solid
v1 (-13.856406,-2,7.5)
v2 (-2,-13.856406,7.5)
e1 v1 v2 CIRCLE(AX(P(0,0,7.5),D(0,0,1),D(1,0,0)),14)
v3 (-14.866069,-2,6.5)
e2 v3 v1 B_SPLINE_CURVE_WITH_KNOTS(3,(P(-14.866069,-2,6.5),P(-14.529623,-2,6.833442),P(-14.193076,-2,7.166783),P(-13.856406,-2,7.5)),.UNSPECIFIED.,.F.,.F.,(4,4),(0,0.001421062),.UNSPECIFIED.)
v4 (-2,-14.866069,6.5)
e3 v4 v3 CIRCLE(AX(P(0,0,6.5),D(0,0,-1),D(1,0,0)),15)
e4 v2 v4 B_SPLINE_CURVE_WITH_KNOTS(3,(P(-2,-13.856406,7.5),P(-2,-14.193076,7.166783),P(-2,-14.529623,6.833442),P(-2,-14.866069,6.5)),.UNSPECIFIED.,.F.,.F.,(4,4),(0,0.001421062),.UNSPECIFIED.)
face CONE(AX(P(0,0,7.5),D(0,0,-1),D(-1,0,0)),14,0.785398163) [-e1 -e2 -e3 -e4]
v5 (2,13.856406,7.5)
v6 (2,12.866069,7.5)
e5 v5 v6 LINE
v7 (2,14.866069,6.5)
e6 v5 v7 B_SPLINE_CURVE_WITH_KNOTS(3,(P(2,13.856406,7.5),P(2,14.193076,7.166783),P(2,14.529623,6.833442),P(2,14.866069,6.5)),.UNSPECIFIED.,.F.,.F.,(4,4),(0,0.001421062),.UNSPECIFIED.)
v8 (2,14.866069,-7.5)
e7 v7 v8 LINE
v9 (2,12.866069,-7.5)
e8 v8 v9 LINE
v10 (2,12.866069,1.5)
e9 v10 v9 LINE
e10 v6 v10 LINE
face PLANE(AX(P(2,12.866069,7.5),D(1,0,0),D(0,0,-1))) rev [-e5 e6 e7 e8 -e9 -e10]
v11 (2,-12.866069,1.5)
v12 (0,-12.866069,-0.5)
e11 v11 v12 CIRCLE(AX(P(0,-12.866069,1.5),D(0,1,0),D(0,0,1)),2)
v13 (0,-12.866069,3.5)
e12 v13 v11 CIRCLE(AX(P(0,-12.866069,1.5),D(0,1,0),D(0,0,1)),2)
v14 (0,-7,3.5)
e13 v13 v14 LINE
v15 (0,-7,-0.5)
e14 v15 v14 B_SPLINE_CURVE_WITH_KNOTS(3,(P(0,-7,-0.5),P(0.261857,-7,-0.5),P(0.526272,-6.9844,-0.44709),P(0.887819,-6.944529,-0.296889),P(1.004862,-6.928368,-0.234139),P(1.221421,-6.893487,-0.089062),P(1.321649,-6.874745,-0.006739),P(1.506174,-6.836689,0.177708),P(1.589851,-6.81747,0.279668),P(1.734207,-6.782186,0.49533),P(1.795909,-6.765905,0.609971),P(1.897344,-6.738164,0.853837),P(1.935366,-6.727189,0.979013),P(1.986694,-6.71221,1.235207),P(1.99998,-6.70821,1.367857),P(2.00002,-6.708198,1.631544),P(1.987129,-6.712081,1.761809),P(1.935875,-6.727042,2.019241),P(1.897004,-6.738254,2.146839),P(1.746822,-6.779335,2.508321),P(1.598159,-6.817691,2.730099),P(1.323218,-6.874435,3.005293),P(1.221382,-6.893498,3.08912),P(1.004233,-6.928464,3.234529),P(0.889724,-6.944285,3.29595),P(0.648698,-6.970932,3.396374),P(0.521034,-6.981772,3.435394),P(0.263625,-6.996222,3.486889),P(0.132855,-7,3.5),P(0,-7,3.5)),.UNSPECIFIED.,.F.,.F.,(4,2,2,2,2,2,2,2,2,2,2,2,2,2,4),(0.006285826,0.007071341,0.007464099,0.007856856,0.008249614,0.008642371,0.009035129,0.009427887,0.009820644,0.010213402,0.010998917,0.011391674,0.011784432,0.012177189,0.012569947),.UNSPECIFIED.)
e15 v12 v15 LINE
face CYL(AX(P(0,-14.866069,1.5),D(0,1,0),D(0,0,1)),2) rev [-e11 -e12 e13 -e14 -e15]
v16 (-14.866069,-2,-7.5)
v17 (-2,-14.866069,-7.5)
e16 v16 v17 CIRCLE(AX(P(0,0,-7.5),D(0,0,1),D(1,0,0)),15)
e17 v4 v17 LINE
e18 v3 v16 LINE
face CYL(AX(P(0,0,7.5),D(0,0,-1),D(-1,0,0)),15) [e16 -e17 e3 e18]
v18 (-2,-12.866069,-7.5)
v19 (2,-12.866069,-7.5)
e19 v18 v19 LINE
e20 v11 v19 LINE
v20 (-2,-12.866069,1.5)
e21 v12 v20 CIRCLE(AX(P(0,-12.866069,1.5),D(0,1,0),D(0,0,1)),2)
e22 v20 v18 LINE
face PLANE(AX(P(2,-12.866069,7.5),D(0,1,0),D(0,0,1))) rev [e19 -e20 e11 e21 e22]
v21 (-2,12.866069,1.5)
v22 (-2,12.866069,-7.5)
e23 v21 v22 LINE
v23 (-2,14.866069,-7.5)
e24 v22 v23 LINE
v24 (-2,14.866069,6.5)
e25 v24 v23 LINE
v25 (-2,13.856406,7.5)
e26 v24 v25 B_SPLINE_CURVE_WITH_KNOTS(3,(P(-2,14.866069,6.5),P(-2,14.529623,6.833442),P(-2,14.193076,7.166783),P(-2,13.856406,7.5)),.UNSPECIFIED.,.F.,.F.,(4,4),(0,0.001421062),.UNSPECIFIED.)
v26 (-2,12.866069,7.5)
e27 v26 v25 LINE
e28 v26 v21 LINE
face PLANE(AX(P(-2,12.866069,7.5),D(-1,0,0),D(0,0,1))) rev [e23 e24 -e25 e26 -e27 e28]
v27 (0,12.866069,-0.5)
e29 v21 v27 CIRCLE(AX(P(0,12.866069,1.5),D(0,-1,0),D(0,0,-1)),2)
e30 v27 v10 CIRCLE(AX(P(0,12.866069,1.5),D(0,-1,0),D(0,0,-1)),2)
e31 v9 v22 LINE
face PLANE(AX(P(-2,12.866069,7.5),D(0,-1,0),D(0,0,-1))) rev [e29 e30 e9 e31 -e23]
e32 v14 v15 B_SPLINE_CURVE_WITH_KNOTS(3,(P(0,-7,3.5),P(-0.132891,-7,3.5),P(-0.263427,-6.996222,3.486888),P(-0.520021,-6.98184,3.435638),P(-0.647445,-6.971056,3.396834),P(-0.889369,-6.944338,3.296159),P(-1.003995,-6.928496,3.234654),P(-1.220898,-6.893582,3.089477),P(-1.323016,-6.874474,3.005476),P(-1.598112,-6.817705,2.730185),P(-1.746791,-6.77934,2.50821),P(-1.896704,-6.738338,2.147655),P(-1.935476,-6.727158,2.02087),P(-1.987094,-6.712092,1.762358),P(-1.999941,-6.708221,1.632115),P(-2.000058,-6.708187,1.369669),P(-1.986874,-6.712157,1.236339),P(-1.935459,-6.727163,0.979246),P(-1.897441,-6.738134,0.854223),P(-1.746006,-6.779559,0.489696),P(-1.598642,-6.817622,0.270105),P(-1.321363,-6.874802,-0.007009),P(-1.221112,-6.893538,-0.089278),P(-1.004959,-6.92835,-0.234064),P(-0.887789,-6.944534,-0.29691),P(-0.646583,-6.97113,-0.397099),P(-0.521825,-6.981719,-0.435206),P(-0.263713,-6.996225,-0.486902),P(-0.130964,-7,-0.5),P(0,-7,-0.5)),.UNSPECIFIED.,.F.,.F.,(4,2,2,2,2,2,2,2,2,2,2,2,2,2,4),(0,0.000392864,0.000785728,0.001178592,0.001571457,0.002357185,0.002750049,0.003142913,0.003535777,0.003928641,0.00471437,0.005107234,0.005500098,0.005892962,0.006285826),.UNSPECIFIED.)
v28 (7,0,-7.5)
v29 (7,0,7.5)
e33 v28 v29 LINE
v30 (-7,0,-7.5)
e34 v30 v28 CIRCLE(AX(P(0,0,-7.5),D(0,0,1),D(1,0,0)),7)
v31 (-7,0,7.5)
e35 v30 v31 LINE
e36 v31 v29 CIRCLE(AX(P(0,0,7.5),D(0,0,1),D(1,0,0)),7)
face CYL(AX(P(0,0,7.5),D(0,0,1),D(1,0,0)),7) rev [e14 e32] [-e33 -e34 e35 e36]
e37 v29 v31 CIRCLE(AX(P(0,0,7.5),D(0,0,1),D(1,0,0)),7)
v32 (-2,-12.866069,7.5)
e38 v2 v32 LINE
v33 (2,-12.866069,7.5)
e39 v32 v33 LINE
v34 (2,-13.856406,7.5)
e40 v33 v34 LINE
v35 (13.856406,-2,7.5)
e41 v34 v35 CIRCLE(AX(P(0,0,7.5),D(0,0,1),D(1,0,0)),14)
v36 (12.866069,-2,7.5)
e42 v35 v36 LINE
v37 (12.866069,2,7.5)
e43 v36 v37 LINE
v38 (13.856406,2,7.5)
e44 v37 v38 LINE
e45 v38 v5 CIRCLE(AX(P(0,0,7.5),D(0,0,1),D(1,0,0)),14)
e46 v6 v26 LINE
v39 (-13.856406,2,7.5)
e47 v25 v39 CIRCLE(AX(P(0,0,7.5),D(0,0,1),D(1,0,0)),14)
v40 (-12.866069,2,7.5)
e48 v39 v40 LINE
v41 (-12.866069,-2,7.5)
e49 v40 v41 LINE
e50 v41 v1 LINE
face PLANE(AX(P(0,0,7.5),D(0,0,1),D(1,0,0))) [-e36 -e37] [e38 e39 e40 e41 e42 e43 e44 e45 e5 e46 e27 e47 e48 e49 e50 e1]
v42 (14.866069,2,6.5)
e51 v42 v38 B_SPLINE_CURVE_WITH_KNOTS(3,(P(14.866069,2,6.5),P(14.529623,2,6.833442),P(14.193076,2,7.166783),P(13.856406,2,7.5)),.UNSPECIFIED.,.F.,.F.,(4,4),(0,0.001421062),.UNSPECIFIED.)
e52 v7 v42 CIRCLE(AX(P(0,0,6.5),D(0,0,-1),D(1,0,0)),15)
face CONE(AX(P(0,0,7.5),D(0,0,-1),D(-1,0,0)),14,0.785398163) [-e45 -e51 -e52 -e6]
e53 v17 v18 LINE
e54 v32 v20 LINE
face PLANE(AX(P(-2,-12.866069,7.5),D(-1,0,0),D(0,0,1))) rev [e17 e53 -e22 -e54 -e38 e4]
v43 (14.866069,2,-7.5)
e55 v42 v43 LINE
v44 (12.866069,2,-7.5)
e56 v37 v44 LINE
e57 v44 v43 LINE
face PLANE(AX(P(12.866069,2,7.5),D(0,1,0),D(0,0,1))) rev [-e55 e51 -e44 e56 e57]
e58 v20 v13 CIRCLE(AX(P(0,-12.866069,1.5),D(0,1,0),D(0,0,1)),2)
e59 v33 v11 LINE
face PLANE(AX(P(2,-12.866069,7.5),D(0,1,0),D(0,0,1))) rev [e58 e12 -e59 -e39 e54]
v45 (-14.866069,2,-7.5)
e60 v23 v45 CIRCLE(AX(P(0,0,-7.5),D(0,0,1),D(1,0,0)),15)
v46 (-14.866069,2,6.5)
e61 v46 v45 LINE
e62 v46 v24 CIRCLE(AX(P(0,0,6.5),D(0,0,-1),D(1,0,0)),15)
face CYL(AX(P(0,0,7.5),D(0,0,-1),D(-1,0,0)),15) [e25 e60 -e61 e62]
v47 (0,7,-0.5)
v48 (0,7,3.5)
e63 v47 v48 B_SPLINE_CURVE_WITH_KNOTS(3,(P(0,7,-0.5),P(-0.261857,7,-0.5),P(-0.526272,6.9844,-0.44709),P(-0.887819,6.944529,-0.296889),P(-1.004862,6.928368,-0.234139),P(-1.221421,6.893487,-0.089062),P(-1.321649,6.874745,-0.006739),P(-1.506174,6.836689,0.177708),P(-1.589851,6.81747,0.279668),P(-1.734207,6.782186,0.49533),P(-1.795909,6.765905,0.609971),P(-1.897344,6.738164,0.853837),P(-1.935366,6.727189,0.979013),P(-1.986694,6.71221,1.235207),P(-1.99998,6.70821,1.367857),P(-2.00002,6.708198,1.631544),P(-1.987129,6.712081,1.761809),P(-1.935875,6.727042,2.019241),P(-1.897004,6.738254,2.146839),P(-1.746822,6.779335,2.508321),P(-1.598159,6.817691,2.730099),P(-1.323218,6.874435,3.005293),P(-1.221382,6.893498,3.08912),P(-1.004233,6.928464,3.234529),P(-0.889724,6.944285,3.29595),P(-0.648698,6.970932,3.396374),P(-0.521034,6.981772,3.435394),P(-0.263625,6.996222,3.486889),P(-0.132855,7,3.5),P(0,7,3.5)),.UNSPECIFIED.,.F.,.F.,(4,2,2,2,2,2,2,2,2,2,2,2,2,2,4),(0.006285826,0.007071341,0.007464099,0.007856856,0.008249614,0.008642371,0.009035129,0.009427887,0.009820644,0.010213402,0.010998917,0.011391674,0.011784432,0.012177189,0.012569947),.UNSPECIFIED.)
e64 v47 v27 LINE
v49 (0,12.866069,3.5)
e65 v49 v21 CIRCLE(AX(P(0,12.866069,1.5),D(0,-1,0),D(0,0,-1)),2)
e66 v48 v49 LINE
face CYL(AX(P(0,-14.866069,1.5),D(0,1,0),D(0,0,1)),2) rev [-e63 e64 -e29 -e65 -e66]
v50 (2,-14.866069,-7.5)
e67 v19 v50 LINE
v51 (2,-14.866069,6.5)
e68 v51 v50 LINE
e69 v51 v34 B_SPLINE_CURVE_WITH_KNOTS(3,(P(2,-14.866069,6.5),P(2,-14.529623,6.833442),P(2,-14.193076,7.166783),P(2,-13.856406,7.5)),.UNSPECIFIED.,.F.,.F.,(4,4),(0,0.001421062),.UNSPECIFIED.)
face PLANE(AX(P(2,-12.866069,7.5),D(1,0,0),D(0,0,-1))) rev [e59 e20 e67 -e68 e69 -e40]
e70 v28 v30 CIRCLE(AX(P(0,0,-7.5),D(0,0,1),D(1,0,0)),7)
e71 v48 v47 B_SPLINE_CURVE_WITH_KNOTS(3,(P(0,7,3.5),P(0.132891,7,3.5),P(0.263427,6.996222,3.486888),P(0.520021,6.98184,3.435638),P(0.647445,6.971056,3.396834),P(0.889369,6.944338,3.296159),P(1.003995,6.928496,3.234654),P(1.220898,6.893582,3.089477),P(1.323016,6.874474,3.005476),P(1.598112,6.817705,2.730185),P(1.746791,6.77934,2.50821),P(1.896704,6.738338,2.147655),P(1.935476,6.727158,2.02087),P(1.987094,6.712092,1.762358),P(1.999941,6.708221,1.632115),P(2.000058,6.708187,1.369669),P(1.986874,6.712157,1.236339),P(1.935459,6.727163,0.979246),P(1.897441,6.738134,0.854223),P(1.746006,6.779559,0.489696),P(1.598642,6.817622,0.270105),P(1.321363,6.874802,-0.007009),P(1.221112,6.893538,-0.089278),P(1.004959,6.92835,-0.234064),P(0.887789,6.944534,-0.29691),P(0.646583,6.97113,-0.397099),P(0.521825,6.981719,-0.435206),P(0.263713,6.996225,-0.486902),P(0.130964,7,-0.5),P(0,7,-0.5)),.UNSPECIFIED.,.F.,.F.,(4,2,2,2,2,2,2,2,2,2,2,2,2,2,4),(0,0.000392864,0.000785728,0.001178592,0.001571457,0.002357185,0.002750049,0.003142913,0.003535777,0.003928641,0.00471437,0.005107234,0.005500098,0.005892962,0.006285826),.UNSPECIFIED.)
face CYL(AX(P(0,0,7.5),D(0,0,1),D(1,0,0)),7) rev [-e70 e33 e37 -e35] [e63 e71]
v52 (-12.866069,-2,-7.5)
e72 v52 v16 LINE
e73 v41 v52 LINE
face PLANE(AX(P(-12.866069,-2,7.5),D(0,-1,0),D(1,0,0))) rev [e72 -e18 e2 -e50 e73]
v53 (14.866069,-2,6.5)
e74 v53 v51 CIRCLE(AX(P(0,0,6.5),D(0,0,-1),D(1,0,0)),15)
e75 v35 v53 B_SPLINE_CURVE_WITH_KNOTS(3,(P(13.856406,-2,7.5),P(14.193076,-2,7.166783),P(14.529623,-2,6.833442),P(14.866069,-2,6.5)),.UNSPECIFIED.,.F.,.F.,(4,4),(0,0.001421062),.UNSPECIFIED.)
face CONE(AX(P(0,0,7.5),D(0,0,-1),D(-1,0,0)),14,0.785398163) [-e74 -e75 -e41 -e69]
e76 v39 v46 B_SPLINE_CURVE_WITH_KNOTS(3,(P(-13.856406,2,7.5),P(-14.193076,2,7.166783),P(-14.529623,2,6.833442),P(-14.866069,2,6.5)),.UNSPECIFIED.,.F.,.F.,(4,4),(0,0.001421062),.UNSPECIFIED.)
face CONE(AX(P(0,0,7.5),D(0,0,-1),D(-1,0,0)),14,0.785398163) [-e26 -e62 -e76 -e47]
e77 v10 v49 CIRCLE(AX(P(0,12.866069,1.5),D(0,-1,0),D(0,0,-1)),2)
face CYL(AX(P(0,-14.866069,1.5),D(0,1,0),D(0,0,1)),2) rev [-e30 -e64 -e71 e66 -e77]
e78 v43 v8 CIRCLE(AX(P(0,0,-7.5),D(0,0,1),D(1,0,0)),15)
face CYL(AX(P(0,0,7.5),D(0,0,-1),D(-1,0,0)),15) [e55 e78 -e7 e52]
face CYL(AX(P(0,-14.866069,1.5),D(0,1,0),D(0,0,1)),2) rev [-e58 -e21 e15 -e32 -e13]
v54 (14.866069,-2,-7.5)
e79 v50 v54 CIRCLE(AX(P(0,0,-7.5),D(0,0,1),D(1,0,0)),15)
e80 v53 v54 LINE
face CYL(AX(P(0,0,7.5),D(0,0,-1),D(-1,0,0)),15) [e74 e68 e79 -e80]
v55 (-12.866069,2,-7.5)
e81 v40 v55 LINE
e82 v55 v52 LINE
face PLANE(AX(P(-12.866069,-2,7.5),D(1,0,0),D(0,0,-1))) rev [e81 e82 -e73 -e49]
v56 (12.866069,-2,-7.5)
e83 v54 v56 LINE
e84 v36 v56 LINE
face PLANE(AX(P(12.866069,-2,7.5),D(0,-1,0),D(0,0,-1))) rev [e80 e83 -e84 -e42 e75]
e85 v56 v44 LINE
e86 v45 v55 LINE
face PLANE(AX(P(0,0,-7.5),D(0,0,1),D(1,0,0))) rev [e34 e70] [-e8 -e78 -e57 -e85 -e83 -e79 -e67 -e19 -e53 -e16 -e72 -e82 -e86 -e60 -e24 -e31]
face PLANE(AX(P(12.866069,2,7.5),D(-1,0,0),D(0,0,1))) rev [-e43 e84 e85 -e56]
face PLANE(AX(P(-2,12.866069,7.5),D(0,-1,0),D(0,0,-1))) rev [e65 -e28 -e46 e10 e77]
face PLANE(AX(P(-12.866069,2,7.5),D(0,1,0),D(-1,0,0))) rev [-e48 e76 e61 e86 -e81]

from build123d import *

# Parameters (mm, degrees)
NUT_BODY_15MM_DEPTH       = 7.5
M16_TAPPED_THROUGH_HOLE_D = 14
EDGE_CHAMFER_1X45_SIZE    = 1
CROSS_HOLE_4_DEPTH        = 23.321514286
CROSS_HOLE_4_DEPTH_BACK   = 23.321514286
CROSS_HOLE_4_SKETCH_R     = 2


with BuildPart() as part:
    # Slotted Nut Profile Ø30 → Nut Body 15mm (new, symmetric)
    with BuildSketch(Plane.XY):
        with BuildLine():
            Line((2, 12.866068747), (2, 14.866068747))
            ThreePointArc((2, 14.866068747), (10.606601718, 10.606601718), (14.866068747, 2))
            Line((14.866068747, 2), (12.866068747, 2))
            Line((12.866068747, 2), (12.866068747, -2))
            Line((12.866068747, -2), (14.866068747, -2))
            ThreePointArc((14.866068747, -2), (10.606601718, -10.606601718), (2, -14.866068747))
            Line((2, -14.866068747), (2, -12.866068747))
            Line((2, -12.866068747), (-2, -12.866068747))
            Line((-2, -12.866068747), (-2, -14.866068747))
            ThreePointArc((-2, -14.866068747), (-10.606601718, -10.606601718), (-14.866068747, -2))
            Line((-14.866068747, -2), (-12.866068747, -2))
            Line((-12.866068747, -2), (-12.866068747, 2))
            Line((-12.866068747, 2), (-14.866068747, 2))
            ThreePointArc((-14.866068747, 2), (-10.606601718, 10.606601718), (-2, 14.866068747))
            Line((-2, 14.866068747), (-2, 12.866068747))
            Line((-2, 12.866068747), (2, 12.866068747))
        make_face()
    extrude(amount=NUT_BODY_15MM_DEPTH, both=True)

    # M16 Tapped Through Hole (through all)
    with Locations(Plane.XY.offset(7.5)):
        with Locations((0, 0)):
            Hole(M16_TAPPED_THROUGH_HOLE_D / 2)

    # Edge Chamfer 1x45°
    edge_chamfer_1x45_edges = [part.edges().sort_by_distance(p)[0] for p in [
        (-10.606601718, 10.606601718, 7.5),
        (-10.606601718, -10.606601718, 7.5),
        (10.606601718, -10.606601718, 7.5),
        (10.606601718, 10.606601718, 7.5),
    ]]
    chamfer(edge_chamfer_1x45_edges, length=EDGE_CHAMFER_1X45_SIZE)

    # Cross Hole Ø4 Sketch → Cross Hole Ø4 (cut, two sides: drawn at the far end of the back side and taken through both)
    with BuildSketch(Plane(origin=(0, 0, 0), x_dir=(1, 0, 0), z_dir=(0, 1, 0)).offset(-CROSS_HOLE_4_DEPTH_BACK)):
        with Locations(Location((0, -1.5, 0), (0, 0, 270))):
            Circle(CROSS_HOLE_4_SKETCH_R)
    extrude(amount=CROSS_HOLE_4_DEPTH + CROSS_HOLE_4_DEPTH_BACK, mode=Mode.SUBTRACT)


solid = part.part
